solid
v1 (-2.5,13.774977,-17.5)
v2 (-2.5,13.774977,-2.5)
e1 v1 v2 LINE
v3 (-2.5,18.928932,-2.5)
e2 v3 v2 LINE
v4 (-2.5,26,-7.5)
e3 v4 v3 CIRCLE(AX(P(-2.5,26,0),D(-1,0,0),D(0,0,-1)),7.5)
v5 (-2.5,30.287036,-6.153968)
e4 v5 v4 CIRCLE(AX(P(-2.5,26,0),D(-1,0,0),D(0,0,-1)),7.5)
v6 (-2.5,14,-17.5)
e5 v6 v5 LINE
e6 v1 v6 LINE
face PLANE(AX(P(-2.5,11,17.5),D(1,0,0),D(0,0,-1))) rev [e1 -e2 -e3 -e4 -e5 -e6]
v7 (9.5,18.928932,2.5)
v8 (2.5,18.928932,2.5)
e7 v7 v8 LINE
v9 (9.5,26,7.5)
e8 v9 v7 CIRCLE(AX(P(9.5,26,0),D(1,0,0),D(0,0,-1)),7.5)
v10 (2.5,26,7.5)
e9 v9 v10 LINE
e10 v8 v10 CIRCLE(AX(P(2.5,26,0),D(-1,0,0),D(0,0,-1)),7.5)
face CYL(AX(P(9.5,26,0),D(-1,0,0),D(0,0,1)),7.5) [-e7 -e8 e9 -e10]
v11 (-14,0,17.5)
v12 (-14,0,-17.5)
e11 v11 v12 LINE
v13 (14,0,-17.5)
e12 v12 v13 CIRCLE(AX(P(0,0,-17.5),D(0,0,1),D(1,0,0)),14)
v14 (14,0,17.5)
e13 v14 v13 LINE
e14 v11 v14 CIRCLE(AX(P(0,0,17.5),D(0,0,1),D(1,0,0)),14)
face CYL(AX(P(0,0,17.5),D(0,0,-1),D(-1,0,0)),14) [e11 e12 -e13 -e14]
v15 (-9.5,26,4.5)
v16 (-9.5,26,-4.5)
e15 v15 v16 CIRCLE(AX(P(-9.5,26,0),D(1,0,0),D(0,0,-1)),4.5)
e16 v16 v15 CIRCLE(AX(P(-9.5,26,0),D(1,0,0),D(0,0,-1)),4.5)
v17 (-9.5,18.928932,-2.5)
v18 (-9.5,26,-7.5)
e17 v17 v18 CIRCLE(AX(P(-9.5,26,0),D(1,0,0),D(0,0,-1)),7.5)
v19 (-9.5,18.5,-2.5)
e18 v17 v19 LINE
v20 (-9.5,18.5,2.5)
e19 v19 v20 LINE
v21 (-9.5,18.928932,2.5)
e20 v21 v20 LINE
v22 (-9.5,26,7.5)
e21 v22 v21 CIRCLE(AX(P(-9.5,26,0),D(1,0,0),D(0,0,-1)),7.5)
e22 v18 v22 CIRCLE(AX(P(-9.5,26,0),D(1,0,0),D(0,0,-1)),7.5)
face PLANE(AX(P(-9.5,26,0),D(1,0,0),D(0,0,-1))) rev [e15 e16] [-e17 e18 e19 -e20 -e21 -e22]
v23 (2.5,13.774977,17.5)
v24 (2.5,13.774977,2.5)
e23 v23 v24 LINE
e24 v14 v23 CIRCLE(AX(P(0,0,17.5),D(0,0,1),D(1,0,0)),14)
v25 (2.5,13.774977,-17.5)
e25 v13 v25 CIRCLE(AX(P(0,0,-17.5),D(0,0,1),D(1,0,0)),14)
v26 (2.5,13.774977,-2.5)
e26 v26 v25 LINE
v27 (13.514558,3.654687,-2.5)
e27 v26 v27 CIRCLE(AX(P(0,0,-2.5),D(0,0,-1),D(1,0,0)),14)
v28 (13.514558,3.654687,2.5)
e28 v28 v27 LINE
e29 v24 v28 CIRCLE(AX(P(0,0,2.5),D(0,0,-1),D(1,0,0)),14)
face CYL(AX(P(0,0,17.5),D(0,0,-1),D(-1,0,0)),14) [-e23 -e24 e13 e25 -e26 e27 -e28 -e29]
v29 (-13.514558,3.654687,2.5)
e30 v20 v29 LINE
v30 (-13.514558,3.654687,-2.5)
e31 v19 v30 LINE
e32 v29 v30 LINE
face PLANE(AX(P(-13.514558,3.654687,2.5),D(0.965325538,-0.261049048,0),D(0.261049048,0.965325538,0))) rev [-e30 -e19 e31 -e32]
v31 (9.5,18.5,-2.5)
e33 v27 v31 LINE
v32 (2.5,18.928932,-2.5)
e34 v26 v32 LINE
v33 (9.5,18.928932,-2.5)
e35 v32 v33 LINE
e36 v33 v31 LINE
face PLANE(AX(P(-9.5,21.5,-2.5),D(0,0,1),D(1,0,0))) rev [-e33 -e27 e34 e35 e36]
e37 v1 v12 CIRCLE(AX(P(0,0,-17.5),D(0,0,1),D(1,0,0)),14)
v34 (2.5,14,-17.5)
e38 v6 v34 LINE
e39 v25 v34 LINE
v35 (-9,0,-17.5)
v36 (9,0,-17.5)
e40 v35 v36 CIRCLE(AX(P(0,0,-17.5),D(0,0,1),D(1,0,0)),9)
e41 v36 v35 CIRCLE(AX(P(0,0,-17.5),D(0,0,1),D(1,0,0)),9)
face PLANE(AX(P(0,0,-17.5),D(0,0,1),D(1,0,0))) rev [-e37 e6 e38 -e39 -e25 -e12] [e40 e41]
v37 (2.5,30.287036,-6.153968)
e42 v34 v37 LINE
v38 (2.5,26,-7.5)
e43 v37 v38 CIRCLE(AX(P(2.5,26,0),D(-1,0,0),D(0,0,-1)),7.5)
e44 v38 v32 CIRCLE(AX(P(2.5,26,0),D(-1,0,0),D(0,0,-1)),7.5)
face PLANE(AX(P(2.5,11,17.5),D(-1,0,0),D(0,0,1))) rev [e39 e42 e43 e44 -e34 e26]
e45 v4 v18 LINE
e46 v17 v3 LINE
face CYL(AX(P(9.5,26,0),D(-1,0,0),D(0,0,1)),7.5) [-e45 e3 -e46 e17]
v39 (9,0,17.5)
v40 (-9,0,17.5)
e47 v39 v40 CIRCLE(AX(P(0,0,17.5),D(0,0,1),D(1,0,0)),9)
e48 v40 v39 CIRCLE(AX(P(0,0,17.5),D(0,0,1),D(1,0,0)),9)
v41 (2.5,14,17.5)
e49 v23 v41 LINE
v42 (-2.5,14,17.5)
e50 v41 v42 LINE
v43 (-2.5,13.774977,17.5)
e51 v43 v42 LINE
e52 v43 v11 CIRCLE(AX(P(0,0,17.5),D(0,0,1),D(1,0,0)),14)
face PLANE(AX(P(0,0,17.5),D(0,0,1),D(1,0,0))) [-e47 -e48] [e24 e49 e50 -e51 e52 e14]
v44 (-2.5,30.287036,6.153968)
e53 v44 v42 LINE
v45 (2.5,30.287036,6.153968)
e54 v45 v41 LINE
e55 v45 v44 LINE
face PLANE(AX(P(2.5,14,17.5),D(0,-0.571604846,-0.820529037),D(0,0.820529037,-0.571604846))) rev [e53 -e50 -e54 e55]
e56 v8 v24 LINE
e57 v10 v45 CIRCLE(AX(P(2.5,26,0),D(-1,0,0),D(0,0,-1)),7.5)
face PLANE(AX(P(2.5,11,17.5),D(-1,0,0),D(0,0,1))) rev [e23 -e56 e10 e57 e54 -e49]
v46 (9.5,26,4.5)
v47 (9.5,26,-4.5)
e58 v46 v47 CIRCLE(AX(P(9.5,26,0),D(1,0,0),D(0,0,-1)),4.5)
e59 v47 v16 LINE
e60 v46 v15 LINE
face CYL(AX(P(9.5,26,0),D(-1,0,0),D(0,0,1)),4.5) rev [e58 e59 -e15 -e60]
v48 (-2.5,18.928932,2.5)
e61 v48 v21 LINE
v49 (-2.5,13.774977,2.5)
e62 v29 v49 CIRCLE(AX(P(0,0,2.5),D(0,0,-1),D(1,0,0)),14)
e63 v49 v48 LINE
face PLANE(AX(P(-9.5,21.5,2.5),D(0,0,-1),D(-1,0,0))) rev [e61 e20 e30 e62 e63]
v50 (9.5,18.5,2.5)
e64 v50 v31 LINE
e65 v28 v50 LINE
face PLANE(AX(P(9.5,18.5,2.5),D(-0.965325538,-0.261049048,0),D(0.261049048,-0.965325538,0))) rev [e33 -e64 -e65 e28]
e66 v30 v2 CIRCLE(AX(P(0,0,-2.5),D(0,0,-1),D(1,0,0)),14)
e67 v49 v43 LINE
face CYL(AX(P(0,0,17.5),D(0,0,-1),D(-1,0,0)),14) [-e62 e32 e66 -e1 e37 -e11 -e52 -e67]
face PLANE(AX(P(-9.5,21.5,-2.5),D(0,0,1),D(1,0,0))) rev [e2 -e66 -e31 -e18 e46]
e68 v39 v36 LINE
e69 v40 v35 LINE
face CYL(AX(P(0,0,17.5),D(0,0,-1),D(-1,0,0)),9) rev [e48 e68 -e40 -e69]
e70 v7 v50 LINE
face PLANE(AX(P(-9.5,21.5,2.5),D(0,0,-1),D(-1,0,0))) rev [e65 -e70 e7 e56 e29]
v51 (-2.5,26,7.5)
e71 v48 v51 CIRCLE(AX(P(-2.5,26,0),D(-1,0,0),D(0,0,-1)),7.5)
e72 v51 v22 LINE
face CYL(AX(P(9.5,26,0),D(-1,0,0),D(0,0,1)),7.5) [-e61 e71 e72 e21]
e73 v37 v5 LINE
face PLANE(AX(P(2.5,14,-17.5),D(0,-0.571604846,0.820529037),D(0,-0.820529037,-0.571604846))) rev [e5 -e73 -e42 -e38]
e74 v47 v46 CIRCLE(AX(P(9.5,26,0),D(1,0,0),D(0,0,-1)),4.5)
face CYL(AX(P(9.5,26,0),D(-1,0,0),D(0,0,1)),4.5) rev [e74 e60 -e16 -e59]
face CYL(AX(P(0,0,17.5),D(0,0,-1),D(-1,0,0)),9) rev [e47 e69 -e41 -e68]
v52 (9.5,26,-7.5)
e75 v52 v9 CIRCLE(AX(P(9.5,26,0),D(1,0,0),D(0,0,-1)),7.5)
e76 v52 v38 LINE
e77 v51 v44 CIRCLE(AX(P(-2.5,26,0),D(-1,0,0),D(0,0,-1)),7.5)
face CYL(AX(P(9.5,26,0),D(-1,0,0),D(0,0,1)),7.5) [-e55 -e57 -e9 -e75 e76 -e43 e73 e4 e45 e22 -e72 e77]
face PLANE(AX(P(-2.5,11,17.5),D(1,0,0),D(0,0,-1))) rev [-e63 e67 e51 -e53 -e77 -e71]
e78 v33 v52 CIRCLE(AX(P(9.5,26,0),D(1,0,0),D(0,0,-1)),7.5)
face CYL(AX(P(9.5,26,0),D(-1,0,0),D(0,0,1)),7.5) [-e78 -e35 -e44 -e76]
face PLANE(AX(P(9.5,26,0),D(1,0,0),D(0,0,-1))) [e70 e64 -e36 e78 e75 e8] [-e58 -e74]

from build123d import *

# Parameters (mm, degrees)
MAIN_BORE_PROFILE_28_18_R   = 14
MAIN_BORE_PROFILE_28_18_R_2 = 9
MAIN_BORE_TUBE_28X35_DEPTH  = 17.5
PIVOT_BOSS_PROFILE_15_9_R   = 7.5
PIVOT_BOSS_PROFILE_15_9_R_2 = 4.5
PIVOT_BOSS_15X19_DEPTH      = 9.5
SIDE_RIB_5MM_DEPTH          = 2.5
FRONT_RIB_5MM_DEPTH         = 2.5
FRONT_RIB_PAD_PROFILE_W     = 19
FRONT_RIB_PAD_PROFILE_H     = 5
FRONT_RIB_PAD_3MM_DEPTH     = 3
SIDE_RIB_PAD_PROFILE_W      = 5
SIDE_RIB_PAD_PROFILE_H      = 35
SIDE_RIB_PAD_3MM_DEPTH      = 3


with BuildPart() as part:
    # Main Bore Profile Ø28-Ø18 → Main Bore Tube Ø28x35 (new, symmetric)
    with BuildSketch(Plane.XY):
        Circle(MAIN_BORE_PROFILE_28_18_R)
        Circle(MAIN_BORE_PROFILE_28_18_R_2, mode=Mode.SUBTRACT)
    extrude(amount=MAIN_BORE_TUBE_28X35_DEPTH, both=True)



with BuildPart() as body_2:
    # Pivot Boss Profile Ø15-Ø9 → Pivot Boss Ø15x19 (new, symmetric)
    with BuildSketch(Plane(origin=(0, 0, 0), x_dir=(0, 0, -1), z_dir=(1, 0, 0))):
        with Locations((0, 26)):
            Circle(PIVOT_BOSS_PROFILE_15_9_R)
        with Locations((0, 26)):
            Circle(PIVOT_BOSS_PROFILE_15_9_R_2, mode=Mode.SUBTRACT)
    extrude(amount=PIVOT_BOSS_15X19_DEPTH, both=True)

    # Side Rib Profile → Side Rib 5mm (add, symmetric)
    with BuildSketch(Plane(origin=(0, 0, 0), x_dir=(0, 0, -1), z_dir=(1, 0, 0))):
        with BuildLine():
            Line((-17.5, 14), (-6.153967777, 30.287036342))
            ThreePointArc((-6.153967777, 30.287036342), (0, 18.5), (6.153967777, 30.287036342))
            Line((6.153967777, 30.287036342), (17.5, 14))
            Line((17.5, 14), (-17.5, 14))
        make_face()
    extrude(amount=SIDE_RIB_5MM_DEPTH, both=True)



with BuildPart() as body_3:
    # Front Rib Profile → Front Rib 5mm (new, symmetric)
    with BuildSketch(Plane.XY):
        with BuildLine():
            Line((-13.514557534, 3.654686672), (-9.5, 18.5))
            Line((-9.5, 18.5), (9.5, 18.5))
            Line((9.5, 18.5), (13.514557534, 3.654686672))
            ThreePointArc((13.514557534, 3.654686672), (0, 14), (-13.514557534, 3.654686672))
        make_face()
    extrude(amount=FRONT_RIB_5MM_DEPTH, both=True)


with BuildPart() as body_2_1:
    add(body_2.part)

    add(body_3.part)  # Front Rib Pad 3mm merges body 3
    # Front Rib Pad Profile → Front Rib Pad 3mm (add)
    with BuildSketch(Plane(origin=(0, 18.5, 0), x_dir=(1, 0, 0), z_dir=(0, 1, 0))):
        Rectangle(FRONT_RIB_PAD_PROFILE_W, FRONT_RIB_PAD_PROFILE_H)
    extrude(amount=FRONT_RIB_PAD_3MM_DEPTH)


with BuildPart() as part_1:
    add(part.part)

    add(body_2_1.part)  # Side Rib Pad 3mm merges body 2
    # Side Rib Pad Profile → Side Rib Pad 3mm (add)
    with BuildSketch(Plane.XZ.offset(-14)):
        Rectangle(SIDE_RIB_PAD_PROFILE_W, SIDE_RIB_PAD_PROFILE_H)
    extrude(amount=SIDE_RIB_PAD_3MM_DEPTH)


solid = part_1.part
